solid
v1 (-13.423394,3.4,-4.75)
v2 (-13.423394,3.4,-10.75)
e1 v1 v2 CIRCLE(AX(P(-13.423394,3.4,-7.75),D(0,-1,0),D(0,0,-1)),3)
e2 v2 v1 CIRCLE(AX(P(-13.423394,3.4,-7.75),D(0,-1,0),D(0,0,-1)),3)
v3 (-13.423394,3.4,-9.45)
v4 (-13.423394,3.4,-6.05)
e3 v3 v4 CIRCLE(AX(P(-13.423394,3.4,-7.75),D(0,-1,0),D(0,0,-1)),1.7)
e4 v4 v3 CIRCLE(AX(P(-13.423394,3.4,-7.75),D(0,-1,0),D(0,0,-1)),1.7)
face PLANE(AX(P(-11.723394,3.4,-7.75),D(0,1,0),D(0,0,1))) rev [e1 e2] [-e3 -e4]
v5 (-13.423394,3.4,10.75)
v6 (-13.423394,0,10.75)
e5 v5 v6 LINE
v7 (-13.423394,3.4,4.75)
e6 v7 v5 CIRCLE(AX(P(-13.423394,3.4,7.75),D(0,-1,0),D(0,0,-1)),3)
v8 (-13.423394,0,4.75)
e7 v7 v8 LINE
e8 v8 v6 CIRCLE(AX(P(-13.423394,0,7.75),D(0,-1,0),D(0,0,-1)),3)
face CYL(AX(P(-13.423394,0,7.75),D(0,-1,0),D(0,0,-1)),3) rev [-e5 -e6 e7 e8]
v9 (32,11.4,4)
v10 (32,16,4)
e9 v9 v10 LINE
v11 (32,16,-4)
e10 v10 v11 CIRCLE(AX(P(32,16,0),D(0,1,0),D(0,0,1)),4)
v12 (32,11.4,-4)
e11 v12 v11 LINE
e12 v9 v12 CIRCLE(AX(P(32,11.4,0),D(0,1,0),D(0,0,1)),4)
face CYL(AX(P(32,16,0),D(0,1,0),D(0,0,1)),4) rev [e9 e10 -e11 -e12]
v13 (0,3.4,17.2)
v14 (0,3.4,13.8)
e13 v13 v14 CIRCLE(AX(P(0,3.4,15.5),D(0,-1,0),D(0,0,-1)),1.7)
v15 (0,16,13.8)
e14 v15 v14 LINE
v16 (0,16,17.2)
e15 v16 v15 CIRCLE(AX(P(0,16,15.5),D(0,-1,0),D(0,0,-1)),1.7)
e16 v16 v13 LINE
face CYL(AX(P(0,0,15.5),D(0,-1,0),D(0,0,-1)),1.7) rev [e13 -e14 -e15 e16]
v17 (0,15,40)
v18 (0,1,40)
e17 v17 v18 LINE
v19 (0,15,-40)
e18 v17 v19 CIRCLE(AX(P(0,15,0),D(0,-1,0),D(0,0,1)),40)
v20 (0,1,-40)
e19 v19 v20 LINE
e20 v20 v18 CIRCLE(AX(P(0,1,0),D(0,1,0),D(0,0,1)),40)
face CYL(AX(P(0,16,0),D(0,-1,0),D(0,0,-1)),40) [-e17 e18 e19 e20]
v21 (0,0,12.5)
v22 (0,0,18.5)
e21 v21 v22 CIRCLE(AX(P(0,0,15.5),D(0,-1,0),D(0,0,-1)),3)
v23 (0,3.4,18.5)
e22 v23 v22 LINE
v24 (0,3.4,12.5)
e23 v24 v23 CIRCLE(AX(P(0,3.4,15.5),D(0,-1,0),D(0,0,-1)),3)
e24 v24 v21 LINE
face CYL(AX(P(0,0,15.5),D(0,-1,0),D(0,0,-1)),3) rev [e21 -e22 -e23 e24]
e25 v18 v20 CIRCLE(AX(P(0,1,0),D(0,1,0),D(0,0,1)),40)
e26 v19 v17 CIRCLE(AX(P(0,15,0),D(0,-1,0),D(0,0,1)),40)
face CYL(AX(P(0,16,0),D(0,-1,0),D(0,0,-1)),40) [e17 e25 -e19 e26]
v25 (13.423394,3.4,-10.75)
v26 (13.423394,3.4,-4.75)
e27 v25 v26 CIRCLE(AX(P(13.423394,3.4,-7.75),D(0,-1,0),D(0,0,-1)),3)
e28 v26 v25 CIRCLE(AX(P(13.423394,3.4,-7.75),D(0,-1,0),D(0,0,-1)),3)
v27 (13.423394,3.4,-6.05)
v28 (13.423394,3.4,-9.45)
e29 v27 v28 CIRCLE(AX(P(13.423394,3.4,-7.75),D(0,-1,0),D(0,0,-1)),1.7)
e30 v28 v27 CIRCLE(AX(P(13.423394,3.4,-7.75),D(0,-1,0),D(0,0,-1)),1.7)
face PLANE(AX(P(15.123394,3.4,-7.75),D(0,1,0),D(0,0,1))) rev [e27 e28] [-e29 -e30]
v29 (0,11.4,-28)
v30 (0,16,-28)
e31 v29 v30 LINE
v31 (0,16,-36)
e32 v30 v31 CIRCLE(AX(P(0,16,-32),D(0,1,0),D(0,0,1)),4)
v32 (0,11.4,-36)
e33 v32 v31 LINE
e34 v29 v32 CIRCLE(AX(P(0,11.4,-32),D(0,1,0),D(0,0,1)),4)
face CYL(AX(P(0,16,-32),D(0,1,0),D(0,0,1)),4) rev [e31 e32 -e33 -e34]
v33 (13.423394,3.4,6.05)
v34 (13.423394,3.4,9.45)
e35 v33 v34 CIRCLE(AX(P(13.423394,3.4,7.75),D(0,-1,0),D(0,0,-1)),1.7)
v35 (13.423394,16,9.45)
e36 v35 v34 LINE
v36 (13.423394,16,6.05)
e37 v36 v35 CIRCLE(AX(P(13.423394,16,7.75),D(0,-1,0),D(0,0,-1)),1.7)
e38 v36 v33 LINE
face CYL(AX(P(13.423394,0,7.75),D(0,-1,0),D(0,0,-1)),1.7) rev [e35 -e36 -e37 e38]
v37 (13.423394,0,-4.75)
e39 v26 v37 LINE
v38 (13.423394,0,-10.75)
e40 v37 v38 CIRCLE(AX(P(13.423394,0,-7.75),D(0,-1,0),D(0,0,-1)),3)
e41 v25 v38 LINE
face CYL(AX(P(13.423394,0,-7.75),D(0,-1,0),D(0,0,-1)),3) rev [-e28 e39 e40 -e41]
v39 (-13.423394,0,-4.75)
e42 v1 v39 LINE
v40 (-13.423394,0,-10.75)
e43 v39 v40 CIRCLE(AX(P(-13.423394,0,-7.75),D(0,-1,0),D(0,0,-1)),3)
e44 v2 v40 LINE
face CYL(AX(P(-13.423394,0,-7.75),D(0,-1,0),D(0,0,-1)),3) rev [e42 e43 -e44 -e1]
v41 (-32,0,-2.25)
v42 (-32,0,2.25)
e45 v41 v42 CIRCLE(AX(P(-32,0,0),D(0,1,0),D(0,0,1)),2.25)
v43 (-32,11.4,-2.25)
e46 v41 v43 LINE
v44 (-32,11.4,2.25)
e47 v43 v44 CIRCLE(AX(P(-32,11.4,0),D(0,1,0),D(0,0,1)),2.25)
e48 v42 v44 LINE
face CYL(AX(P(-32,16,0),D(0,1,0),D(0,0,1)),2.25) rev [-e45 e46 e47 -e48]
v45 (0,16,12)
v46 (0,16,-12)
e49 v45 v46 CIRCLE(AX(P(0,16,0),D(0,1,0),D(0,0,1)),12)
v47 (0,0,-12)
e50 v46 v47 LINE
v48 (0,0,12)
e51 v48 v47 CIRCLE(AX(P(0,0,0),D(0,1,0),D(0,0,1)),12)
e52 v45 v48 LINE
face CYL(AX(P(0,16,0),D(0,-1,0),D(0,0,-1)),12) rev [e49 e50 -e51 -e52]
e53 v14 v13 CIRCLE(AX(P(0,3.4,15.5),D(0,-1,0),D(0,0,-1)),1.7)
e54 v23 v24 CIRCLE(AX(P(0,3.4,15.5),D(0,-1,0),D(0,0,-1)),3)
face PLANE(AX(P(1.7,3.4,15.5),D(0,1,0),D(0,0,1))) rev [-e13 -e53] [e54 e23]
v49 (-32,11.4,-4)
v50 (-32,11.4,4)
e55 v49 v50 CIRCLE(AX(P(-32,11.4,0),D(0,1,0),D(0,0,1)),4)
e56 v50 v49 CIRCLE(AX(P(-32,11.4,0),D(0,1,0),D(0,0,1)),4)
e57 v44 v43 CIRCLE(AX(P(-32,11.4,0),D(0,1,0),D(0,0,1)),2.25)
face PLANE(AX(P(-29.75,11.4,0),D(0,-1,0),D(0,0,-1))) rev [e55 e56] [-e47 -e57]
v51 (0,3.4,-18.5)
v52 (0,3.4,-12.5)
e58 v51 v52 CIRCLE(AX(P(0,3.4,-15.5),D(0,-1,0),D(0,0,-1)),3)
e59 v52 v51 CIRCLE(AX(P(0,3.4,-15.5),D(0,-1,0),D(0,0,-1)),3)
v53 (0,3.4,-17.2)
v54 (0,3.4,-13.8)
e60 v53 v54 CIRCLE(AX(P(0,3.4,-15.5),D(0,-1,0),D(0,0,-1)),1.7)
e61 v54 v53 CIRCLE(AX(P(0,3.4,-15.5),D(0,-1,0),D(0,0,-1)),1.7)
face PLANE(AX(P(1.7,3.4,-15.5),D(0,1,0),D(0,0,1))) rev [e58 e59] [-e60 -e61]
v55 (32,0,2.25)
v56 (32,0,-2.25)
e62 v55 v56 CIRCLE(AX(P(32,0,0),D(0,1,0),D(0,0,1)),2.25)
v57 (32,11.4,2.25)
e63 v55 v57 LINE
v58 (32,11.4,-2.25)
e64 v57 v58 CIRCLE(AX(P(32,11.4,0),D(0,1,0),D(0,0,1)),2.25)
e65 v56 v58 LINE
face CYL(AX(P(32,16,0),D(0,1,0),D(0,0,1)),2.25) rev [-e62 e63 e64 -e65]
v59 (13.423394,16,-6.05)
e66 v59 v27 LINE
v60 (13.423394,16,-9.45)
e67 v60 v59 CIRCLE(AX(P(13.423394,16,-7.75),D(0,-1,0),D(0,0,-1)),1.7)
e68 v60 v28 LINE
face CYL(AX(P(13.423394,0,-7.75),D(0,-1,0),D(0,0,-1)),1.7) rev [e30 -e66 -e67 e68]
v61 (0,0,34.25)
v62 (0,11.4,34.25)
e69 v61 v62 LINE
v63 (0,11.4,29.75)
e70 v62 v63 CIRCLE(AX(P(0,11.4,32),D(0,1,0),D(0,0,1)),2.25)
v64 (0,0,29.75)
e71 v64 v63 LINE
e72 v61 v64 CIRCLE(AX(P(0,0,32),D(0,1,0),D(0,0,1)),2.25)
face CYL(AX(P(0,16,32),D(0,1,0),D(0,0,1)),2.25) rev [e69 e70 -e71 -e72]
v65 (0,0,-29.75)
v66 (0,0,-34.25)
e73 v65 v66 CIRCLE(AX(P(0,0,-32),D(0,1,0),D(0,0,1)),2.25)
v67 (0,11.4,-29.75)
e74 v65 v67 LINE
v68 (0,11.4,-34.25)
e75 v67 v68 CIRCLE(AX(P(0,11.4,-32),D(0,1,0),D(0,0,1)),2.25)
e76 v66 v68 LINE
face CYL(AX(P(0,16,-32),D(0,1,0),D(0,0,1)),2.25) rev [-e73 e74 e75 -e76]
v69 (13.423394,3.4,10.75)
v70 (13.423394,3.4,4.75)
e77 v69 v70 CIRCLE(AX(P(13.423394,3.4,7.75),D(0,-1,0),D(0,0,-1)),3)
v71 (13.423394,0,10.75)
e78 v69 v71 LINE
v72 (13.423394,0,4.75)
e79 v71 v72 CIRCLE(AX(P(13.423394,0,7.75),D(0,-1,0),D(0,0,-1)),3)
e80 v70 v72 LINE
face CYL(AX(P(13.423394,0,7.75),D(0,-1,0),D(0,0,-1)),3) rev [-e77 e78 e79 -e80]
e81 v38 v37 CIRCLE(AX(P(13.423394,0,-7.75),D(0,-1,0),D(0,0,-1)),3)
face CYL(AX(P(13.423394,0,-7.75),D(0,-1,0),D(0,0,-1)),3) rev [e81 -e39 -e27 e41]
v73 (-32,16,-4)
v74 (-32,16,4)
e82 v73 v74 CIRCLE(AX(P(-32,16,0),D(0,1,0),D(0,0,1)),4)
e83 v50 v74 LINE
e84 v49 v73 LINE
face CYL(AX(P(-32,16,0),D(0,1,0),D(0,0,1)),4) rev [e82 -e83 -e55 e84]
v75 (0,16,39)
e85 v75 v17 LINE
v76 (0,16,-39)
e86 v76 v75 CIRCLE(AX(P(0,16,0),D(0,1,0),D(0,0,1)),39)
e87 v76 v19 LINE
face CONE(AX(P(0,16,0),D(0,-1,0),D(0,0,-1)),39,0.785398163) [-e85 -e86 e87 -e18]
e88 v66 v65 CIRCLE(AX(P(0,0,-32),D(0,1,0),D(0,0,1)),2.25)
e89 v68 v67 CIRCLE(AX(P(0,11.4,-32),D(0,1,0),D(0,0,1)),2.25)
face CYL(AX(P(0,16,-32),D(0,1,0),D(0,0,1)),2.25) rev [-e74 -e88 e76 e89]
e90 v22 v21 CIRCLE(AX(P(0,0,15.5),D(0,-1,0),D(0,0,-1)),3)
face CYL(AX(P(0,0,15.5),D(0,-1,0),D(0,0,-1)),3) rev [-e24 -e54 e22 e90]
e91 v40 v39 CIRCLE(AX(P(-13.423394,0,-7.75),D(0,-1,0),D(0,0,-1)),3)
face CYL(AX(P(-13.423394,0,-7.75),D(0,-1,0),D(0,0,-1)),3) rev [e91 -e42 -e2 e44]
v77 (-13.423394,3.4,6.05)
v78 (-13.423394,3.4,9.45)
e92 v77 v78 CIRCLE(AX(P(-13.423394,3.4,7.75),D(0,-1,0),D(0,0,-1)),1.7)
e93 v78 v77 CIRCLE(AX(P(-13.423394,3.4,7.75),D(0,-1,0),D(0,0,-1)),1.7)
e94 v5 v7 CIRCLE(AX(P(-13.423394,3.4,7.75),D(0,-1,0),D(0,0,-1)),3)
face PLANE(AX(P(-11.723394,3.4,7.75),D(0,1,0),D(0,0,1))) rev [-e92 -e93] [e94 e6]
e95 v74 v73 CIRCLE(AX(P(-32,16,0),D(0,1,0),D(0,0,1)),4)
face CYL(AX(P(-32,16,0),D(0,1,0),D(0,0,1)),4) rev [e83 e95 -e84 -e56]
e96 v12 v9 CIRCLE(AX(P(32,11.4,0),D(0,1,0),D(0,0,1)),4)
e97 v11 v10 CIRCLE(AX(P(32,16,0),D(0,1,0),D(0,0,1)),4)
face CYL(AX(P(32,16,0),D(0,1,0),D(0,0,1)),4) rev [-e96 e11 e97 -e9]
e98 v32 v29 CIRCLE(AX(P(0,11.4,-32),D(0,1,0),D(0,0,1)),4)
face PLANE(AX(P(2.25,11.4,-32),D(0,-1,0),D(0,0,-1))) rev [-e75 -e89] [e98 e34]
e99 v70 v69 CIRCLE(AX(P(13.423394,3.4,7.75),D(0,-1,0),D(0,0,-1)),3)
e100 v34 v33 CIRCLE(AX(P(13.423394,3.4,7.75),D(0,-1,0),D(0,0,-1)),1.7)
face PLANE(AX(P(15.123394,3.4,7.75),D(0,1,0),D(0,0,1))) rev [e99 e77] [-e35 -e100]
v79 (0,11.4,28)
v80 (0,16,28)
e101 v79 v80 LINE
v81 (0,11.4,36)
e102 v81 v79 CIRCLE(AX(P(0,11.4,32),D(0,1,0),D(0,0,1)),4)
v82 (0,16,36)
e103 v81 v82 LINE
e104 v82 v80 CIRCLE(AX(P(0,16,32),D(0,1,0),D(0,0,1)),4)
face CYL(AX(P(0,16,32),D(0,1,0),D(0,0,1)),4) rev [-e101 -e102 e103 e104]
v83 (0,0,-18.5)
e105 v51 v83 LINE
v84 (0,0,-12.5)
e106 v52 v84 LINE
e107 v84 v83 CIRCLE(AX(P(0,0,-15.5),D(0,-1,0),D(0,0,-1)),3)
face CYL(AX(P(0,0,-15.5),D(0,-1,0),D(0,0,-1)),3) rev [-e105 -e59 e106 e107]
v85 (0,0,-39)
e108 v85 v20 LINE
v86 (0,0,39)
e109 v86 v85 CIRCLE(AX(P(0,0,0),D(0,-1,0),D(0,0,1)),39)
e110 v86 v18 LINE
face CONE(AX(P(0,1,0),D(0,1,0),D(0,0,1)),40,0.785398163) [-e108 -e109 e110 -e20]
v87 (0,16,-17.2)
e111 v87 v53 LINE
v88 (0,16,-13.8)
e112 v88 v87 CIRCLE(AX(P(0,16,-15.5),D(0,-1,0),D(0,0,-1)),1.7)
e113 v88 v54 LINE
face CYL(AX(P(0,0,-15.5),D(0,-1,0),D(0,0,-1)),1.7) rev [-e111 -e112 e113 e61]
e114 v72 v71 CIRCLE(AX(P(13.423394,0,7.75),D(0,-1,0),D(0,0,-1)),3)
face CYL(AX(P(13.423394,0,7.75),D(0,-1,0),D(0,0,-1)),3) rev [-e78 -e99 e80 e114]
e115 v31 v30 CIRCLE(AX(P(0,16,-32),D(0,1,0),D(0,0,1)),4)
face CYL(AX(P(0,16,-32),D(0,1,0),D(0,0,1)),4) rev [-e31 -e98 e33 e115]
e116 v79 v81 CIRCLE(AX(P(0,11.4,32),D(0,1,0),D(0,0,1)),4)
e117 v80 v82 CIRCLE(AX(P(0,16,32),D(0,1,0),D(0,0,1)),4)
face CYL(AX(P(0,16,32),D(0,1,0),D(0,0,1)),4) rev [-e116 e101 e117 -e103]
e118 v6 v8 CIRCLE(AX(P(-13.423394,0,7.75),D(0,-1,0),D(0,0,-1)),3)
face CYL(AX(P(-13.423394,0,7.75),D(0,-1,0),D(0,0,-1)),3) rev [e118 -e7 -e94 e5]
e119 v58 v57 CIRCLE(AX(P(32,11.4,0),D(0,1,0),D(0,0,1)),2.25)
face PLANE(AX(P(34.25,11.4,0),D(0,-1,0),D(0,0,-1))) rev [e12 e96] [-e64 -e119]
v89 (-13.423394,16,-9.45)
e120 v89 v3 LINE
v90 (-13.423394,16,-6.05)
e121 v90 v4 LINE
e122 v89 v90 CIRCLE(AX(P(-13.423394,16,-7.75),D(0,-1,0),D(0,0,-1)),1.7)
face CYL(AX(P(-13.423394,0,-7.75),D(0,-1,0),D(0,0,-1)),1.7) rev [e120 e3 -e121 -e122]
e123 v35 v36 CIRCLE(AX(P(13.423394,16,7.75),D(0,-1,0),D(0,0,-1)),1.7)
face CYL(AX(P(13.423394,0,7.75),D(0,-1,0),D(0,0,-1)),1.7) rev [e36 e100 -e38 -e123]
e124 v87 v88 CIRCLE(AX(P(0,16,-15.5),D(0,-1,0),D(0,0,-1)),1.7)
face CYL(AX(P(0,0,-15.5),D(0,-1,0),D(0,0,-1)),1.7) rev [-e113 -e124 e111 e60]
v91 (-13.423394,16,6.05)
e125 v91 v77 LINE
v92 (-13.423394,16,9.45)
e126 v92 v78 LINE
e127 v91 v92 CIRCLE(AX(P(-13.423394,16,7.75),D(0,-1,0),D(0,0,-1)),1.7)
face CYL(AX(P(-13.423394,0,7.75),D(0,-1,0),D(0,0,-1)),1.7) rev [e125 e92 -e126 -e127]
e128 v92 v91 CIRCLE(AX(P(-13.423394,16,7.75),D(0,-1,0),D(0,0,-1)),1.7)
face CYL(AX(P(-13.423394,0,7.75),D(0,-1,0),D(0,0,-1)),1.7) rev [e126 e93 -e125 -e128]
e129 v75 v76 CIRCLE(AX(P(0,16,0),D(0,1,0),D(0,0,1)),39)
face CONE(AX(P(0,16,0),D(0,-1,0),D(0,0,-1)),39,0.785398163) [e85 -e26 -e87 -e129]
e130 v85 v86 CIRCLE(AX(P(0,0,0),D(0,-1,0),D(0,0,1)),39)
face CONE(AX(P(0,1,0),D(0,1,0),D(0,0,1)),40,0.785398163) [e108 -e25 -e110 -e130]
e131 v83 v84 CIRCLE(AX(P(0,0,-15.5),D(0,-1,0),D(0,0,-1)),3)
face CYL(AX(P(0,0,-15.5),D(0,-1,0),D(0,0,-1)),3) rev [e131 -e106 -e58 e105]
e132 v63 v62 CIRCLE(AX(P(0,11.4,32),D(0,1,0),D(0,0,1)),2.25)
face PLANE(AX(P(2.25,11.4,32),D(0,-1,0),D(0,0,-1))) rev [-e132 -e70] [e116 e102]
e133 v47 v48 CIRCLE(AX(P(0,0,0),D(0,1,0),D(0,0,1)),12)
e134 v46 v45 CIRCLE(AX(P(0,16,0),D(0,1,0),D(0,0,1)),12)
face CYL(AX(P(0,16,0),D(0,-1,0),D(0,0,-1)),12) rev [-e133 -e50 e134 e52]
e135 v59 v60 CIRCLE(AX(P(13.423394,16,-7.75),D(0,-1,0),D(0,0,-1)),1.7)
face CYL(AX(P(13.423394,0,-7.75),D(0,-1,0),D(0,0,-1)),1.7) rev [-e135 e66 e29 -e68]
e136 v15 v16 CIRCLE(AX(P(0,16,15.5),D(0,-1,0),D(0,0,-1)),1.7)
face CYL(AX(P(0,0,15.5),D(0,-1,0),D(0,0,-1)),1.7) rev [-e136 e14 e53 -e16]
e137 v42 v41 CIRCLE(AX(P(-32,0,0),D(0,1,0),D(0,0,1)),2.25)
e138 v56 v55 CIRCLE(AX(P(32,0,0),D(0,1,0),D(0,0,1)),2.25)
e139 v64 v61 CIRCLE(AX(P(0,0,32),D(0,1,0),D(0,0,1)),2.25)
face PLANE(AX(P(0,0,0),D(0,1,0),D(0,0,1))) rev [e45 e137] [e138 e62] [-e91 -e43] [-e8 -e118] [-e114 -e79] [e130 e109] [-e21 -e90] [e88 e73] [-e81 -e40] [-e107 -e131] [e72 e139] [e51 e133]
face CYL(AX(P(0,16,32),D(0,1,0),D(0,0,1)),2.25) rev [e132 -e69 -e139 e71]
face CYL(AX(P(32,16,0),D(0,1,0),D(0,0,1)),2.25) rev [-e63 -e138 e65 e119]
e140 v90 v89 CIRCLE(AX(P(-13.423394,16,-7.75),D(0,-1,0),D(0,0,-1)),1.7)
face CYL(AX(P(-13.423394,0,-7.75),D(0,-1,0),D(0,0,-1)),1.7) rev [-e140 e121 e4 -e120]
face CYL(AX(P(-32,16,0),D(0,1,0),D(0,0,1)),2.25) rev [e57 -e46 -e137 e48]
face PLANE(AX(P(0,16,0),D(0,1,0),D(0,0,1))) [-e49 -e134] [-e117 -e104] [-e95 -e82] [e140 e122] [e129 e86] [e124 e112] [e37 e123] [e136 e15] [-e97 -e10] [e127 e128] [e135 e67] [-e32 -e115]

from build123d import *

# Parameters (mm, degrees)
SKETCH1_R                                          = 40
SKETCH1_R_2                                        = 12
BOSS_EXTRUDE1_DEPTH                                = 16
HOLE_SIZE_BASED_HEX_SOCKET_HEAD_CAP_SC_D           = 3.4
HOLE_SIZE_BASED_HEX_SOCKET_HEAD_CAP_SC_CBORE_D     = 6
HOLE_SIZE_BASED_HEX_SOCKET_HEAD_CAP_SC_CBORE_DEPTH = 3.4
HOLE_SIZE_BASED_HEX_SOCKET_HEAD_CA_2_D             = 4.5
HOLE_SIZE_BASED_HEX_SOCKET_HEAD_CA_2_CBORE_D       = 8
HOLE_SIZE_BASED_HEX_SOCKET_HEAD_CA_2_CBORE_DEPTH   = 4.6
CIRPATTERN1_COUNT                                  = 4
CHAMFER1_SIZE                                      = 1


with BuildPart() as part:
    # Sketch1 → Boss-Extrude1 (new body)
    with BuildSketch(Plane(origin=(0, 0, 0), x_dir=(1, 0, 0), z_dir=(0, 1, 0))):
        with Locations(Location((0, 0, 0), (0, 0, 270))):
            Circle(SKETCH1_R)
        with Locations(Location((0, 0, 0), (0, 0, 270))):
            Circle(SKETCH1_R_2, mode=Mode.SUBTRACT)
    extrude(amount=BOSS_EXTRUDE1_DEPTH)

    # Hole size _based_ hex socket head cap sc (through all)
    with Locations(Plane(origin=(0, 0, 0), x_dir=(-1, 0, 0), z_dir=(0, -1, 0))):
        with Locations((0, -15.5)):
            hole_size_based_hex_socket_head_cap_sc = CounterBoreHole(HOLE_SIZE_BASED_HEX_SOCKET_HEAD_CAP_SC_D / 2, HOLE_SIZE_BASED_HEX_SOCKET_HEAD_CAP_SC_CBORE_D / 2, HOLE_SIZE_BASED_HEX_SOCKET_HEAD_CAP_SC_CBORE_DEPTH)

    # SketchPattern1: Hole size _based_ hex socket head cap sc at 5 more places
    with Locations((13.423394, 0, -23.25), (13.423394, 0, -7.75), (-13.423394, 0, -7.75), (-13.423394, 0, -23.25), (0, 0, -31)):
        add(hole_size_based_hex_socket_head_cap_sc, mode=Mode.SUBTRACT)

    # Hole size _based_ hex socket head ca 2 (through all)
    with Locations(Plane(origin=(0, 16, 0), x_dir=(1, 0, 0), z_dir=(0, 1, 0))):
        with Locations((0, 32)):
            hole_size_based_hex_socket_head_ca_2 = CounterBoreHole(HOLE_SIZE_BASED_HEX_SOCKET_HEAD_CA_2_D / 2, HOLE_SIZE_BASED_HEX_SOCKET_HEAD_CA_2_CBORE_D / 2, HOLE_SIZE_BASED_HEX_SOCKET_HEAD_CA_2_CBORE_DEPTH)

    # CirPattern1: Hole size _based_ hex socket head ca 2 ×4 about axis
    cirpattern1_axis = Axis((0, 0, 0), (0, 1, 0))
    for i in range(1, CIRPATTERN1_COUNT):
        add(hole_size_based_hex_socket_head_ca_2.rotate(cirpattern1_axis, i * 360 / CIRPATTERN1_COUNT), mode=Mode.SUBTRACT)

    # Chamfer1
    chamfer1_edges = [part.edges().sort_by_distance(p)[0] for p in [
        (0, 0, -40),
        (0, 16, -40),
    ]]
    chamfer(chamfer1_edges, length=CHAMFER1_SIZE)


solid = part.part
